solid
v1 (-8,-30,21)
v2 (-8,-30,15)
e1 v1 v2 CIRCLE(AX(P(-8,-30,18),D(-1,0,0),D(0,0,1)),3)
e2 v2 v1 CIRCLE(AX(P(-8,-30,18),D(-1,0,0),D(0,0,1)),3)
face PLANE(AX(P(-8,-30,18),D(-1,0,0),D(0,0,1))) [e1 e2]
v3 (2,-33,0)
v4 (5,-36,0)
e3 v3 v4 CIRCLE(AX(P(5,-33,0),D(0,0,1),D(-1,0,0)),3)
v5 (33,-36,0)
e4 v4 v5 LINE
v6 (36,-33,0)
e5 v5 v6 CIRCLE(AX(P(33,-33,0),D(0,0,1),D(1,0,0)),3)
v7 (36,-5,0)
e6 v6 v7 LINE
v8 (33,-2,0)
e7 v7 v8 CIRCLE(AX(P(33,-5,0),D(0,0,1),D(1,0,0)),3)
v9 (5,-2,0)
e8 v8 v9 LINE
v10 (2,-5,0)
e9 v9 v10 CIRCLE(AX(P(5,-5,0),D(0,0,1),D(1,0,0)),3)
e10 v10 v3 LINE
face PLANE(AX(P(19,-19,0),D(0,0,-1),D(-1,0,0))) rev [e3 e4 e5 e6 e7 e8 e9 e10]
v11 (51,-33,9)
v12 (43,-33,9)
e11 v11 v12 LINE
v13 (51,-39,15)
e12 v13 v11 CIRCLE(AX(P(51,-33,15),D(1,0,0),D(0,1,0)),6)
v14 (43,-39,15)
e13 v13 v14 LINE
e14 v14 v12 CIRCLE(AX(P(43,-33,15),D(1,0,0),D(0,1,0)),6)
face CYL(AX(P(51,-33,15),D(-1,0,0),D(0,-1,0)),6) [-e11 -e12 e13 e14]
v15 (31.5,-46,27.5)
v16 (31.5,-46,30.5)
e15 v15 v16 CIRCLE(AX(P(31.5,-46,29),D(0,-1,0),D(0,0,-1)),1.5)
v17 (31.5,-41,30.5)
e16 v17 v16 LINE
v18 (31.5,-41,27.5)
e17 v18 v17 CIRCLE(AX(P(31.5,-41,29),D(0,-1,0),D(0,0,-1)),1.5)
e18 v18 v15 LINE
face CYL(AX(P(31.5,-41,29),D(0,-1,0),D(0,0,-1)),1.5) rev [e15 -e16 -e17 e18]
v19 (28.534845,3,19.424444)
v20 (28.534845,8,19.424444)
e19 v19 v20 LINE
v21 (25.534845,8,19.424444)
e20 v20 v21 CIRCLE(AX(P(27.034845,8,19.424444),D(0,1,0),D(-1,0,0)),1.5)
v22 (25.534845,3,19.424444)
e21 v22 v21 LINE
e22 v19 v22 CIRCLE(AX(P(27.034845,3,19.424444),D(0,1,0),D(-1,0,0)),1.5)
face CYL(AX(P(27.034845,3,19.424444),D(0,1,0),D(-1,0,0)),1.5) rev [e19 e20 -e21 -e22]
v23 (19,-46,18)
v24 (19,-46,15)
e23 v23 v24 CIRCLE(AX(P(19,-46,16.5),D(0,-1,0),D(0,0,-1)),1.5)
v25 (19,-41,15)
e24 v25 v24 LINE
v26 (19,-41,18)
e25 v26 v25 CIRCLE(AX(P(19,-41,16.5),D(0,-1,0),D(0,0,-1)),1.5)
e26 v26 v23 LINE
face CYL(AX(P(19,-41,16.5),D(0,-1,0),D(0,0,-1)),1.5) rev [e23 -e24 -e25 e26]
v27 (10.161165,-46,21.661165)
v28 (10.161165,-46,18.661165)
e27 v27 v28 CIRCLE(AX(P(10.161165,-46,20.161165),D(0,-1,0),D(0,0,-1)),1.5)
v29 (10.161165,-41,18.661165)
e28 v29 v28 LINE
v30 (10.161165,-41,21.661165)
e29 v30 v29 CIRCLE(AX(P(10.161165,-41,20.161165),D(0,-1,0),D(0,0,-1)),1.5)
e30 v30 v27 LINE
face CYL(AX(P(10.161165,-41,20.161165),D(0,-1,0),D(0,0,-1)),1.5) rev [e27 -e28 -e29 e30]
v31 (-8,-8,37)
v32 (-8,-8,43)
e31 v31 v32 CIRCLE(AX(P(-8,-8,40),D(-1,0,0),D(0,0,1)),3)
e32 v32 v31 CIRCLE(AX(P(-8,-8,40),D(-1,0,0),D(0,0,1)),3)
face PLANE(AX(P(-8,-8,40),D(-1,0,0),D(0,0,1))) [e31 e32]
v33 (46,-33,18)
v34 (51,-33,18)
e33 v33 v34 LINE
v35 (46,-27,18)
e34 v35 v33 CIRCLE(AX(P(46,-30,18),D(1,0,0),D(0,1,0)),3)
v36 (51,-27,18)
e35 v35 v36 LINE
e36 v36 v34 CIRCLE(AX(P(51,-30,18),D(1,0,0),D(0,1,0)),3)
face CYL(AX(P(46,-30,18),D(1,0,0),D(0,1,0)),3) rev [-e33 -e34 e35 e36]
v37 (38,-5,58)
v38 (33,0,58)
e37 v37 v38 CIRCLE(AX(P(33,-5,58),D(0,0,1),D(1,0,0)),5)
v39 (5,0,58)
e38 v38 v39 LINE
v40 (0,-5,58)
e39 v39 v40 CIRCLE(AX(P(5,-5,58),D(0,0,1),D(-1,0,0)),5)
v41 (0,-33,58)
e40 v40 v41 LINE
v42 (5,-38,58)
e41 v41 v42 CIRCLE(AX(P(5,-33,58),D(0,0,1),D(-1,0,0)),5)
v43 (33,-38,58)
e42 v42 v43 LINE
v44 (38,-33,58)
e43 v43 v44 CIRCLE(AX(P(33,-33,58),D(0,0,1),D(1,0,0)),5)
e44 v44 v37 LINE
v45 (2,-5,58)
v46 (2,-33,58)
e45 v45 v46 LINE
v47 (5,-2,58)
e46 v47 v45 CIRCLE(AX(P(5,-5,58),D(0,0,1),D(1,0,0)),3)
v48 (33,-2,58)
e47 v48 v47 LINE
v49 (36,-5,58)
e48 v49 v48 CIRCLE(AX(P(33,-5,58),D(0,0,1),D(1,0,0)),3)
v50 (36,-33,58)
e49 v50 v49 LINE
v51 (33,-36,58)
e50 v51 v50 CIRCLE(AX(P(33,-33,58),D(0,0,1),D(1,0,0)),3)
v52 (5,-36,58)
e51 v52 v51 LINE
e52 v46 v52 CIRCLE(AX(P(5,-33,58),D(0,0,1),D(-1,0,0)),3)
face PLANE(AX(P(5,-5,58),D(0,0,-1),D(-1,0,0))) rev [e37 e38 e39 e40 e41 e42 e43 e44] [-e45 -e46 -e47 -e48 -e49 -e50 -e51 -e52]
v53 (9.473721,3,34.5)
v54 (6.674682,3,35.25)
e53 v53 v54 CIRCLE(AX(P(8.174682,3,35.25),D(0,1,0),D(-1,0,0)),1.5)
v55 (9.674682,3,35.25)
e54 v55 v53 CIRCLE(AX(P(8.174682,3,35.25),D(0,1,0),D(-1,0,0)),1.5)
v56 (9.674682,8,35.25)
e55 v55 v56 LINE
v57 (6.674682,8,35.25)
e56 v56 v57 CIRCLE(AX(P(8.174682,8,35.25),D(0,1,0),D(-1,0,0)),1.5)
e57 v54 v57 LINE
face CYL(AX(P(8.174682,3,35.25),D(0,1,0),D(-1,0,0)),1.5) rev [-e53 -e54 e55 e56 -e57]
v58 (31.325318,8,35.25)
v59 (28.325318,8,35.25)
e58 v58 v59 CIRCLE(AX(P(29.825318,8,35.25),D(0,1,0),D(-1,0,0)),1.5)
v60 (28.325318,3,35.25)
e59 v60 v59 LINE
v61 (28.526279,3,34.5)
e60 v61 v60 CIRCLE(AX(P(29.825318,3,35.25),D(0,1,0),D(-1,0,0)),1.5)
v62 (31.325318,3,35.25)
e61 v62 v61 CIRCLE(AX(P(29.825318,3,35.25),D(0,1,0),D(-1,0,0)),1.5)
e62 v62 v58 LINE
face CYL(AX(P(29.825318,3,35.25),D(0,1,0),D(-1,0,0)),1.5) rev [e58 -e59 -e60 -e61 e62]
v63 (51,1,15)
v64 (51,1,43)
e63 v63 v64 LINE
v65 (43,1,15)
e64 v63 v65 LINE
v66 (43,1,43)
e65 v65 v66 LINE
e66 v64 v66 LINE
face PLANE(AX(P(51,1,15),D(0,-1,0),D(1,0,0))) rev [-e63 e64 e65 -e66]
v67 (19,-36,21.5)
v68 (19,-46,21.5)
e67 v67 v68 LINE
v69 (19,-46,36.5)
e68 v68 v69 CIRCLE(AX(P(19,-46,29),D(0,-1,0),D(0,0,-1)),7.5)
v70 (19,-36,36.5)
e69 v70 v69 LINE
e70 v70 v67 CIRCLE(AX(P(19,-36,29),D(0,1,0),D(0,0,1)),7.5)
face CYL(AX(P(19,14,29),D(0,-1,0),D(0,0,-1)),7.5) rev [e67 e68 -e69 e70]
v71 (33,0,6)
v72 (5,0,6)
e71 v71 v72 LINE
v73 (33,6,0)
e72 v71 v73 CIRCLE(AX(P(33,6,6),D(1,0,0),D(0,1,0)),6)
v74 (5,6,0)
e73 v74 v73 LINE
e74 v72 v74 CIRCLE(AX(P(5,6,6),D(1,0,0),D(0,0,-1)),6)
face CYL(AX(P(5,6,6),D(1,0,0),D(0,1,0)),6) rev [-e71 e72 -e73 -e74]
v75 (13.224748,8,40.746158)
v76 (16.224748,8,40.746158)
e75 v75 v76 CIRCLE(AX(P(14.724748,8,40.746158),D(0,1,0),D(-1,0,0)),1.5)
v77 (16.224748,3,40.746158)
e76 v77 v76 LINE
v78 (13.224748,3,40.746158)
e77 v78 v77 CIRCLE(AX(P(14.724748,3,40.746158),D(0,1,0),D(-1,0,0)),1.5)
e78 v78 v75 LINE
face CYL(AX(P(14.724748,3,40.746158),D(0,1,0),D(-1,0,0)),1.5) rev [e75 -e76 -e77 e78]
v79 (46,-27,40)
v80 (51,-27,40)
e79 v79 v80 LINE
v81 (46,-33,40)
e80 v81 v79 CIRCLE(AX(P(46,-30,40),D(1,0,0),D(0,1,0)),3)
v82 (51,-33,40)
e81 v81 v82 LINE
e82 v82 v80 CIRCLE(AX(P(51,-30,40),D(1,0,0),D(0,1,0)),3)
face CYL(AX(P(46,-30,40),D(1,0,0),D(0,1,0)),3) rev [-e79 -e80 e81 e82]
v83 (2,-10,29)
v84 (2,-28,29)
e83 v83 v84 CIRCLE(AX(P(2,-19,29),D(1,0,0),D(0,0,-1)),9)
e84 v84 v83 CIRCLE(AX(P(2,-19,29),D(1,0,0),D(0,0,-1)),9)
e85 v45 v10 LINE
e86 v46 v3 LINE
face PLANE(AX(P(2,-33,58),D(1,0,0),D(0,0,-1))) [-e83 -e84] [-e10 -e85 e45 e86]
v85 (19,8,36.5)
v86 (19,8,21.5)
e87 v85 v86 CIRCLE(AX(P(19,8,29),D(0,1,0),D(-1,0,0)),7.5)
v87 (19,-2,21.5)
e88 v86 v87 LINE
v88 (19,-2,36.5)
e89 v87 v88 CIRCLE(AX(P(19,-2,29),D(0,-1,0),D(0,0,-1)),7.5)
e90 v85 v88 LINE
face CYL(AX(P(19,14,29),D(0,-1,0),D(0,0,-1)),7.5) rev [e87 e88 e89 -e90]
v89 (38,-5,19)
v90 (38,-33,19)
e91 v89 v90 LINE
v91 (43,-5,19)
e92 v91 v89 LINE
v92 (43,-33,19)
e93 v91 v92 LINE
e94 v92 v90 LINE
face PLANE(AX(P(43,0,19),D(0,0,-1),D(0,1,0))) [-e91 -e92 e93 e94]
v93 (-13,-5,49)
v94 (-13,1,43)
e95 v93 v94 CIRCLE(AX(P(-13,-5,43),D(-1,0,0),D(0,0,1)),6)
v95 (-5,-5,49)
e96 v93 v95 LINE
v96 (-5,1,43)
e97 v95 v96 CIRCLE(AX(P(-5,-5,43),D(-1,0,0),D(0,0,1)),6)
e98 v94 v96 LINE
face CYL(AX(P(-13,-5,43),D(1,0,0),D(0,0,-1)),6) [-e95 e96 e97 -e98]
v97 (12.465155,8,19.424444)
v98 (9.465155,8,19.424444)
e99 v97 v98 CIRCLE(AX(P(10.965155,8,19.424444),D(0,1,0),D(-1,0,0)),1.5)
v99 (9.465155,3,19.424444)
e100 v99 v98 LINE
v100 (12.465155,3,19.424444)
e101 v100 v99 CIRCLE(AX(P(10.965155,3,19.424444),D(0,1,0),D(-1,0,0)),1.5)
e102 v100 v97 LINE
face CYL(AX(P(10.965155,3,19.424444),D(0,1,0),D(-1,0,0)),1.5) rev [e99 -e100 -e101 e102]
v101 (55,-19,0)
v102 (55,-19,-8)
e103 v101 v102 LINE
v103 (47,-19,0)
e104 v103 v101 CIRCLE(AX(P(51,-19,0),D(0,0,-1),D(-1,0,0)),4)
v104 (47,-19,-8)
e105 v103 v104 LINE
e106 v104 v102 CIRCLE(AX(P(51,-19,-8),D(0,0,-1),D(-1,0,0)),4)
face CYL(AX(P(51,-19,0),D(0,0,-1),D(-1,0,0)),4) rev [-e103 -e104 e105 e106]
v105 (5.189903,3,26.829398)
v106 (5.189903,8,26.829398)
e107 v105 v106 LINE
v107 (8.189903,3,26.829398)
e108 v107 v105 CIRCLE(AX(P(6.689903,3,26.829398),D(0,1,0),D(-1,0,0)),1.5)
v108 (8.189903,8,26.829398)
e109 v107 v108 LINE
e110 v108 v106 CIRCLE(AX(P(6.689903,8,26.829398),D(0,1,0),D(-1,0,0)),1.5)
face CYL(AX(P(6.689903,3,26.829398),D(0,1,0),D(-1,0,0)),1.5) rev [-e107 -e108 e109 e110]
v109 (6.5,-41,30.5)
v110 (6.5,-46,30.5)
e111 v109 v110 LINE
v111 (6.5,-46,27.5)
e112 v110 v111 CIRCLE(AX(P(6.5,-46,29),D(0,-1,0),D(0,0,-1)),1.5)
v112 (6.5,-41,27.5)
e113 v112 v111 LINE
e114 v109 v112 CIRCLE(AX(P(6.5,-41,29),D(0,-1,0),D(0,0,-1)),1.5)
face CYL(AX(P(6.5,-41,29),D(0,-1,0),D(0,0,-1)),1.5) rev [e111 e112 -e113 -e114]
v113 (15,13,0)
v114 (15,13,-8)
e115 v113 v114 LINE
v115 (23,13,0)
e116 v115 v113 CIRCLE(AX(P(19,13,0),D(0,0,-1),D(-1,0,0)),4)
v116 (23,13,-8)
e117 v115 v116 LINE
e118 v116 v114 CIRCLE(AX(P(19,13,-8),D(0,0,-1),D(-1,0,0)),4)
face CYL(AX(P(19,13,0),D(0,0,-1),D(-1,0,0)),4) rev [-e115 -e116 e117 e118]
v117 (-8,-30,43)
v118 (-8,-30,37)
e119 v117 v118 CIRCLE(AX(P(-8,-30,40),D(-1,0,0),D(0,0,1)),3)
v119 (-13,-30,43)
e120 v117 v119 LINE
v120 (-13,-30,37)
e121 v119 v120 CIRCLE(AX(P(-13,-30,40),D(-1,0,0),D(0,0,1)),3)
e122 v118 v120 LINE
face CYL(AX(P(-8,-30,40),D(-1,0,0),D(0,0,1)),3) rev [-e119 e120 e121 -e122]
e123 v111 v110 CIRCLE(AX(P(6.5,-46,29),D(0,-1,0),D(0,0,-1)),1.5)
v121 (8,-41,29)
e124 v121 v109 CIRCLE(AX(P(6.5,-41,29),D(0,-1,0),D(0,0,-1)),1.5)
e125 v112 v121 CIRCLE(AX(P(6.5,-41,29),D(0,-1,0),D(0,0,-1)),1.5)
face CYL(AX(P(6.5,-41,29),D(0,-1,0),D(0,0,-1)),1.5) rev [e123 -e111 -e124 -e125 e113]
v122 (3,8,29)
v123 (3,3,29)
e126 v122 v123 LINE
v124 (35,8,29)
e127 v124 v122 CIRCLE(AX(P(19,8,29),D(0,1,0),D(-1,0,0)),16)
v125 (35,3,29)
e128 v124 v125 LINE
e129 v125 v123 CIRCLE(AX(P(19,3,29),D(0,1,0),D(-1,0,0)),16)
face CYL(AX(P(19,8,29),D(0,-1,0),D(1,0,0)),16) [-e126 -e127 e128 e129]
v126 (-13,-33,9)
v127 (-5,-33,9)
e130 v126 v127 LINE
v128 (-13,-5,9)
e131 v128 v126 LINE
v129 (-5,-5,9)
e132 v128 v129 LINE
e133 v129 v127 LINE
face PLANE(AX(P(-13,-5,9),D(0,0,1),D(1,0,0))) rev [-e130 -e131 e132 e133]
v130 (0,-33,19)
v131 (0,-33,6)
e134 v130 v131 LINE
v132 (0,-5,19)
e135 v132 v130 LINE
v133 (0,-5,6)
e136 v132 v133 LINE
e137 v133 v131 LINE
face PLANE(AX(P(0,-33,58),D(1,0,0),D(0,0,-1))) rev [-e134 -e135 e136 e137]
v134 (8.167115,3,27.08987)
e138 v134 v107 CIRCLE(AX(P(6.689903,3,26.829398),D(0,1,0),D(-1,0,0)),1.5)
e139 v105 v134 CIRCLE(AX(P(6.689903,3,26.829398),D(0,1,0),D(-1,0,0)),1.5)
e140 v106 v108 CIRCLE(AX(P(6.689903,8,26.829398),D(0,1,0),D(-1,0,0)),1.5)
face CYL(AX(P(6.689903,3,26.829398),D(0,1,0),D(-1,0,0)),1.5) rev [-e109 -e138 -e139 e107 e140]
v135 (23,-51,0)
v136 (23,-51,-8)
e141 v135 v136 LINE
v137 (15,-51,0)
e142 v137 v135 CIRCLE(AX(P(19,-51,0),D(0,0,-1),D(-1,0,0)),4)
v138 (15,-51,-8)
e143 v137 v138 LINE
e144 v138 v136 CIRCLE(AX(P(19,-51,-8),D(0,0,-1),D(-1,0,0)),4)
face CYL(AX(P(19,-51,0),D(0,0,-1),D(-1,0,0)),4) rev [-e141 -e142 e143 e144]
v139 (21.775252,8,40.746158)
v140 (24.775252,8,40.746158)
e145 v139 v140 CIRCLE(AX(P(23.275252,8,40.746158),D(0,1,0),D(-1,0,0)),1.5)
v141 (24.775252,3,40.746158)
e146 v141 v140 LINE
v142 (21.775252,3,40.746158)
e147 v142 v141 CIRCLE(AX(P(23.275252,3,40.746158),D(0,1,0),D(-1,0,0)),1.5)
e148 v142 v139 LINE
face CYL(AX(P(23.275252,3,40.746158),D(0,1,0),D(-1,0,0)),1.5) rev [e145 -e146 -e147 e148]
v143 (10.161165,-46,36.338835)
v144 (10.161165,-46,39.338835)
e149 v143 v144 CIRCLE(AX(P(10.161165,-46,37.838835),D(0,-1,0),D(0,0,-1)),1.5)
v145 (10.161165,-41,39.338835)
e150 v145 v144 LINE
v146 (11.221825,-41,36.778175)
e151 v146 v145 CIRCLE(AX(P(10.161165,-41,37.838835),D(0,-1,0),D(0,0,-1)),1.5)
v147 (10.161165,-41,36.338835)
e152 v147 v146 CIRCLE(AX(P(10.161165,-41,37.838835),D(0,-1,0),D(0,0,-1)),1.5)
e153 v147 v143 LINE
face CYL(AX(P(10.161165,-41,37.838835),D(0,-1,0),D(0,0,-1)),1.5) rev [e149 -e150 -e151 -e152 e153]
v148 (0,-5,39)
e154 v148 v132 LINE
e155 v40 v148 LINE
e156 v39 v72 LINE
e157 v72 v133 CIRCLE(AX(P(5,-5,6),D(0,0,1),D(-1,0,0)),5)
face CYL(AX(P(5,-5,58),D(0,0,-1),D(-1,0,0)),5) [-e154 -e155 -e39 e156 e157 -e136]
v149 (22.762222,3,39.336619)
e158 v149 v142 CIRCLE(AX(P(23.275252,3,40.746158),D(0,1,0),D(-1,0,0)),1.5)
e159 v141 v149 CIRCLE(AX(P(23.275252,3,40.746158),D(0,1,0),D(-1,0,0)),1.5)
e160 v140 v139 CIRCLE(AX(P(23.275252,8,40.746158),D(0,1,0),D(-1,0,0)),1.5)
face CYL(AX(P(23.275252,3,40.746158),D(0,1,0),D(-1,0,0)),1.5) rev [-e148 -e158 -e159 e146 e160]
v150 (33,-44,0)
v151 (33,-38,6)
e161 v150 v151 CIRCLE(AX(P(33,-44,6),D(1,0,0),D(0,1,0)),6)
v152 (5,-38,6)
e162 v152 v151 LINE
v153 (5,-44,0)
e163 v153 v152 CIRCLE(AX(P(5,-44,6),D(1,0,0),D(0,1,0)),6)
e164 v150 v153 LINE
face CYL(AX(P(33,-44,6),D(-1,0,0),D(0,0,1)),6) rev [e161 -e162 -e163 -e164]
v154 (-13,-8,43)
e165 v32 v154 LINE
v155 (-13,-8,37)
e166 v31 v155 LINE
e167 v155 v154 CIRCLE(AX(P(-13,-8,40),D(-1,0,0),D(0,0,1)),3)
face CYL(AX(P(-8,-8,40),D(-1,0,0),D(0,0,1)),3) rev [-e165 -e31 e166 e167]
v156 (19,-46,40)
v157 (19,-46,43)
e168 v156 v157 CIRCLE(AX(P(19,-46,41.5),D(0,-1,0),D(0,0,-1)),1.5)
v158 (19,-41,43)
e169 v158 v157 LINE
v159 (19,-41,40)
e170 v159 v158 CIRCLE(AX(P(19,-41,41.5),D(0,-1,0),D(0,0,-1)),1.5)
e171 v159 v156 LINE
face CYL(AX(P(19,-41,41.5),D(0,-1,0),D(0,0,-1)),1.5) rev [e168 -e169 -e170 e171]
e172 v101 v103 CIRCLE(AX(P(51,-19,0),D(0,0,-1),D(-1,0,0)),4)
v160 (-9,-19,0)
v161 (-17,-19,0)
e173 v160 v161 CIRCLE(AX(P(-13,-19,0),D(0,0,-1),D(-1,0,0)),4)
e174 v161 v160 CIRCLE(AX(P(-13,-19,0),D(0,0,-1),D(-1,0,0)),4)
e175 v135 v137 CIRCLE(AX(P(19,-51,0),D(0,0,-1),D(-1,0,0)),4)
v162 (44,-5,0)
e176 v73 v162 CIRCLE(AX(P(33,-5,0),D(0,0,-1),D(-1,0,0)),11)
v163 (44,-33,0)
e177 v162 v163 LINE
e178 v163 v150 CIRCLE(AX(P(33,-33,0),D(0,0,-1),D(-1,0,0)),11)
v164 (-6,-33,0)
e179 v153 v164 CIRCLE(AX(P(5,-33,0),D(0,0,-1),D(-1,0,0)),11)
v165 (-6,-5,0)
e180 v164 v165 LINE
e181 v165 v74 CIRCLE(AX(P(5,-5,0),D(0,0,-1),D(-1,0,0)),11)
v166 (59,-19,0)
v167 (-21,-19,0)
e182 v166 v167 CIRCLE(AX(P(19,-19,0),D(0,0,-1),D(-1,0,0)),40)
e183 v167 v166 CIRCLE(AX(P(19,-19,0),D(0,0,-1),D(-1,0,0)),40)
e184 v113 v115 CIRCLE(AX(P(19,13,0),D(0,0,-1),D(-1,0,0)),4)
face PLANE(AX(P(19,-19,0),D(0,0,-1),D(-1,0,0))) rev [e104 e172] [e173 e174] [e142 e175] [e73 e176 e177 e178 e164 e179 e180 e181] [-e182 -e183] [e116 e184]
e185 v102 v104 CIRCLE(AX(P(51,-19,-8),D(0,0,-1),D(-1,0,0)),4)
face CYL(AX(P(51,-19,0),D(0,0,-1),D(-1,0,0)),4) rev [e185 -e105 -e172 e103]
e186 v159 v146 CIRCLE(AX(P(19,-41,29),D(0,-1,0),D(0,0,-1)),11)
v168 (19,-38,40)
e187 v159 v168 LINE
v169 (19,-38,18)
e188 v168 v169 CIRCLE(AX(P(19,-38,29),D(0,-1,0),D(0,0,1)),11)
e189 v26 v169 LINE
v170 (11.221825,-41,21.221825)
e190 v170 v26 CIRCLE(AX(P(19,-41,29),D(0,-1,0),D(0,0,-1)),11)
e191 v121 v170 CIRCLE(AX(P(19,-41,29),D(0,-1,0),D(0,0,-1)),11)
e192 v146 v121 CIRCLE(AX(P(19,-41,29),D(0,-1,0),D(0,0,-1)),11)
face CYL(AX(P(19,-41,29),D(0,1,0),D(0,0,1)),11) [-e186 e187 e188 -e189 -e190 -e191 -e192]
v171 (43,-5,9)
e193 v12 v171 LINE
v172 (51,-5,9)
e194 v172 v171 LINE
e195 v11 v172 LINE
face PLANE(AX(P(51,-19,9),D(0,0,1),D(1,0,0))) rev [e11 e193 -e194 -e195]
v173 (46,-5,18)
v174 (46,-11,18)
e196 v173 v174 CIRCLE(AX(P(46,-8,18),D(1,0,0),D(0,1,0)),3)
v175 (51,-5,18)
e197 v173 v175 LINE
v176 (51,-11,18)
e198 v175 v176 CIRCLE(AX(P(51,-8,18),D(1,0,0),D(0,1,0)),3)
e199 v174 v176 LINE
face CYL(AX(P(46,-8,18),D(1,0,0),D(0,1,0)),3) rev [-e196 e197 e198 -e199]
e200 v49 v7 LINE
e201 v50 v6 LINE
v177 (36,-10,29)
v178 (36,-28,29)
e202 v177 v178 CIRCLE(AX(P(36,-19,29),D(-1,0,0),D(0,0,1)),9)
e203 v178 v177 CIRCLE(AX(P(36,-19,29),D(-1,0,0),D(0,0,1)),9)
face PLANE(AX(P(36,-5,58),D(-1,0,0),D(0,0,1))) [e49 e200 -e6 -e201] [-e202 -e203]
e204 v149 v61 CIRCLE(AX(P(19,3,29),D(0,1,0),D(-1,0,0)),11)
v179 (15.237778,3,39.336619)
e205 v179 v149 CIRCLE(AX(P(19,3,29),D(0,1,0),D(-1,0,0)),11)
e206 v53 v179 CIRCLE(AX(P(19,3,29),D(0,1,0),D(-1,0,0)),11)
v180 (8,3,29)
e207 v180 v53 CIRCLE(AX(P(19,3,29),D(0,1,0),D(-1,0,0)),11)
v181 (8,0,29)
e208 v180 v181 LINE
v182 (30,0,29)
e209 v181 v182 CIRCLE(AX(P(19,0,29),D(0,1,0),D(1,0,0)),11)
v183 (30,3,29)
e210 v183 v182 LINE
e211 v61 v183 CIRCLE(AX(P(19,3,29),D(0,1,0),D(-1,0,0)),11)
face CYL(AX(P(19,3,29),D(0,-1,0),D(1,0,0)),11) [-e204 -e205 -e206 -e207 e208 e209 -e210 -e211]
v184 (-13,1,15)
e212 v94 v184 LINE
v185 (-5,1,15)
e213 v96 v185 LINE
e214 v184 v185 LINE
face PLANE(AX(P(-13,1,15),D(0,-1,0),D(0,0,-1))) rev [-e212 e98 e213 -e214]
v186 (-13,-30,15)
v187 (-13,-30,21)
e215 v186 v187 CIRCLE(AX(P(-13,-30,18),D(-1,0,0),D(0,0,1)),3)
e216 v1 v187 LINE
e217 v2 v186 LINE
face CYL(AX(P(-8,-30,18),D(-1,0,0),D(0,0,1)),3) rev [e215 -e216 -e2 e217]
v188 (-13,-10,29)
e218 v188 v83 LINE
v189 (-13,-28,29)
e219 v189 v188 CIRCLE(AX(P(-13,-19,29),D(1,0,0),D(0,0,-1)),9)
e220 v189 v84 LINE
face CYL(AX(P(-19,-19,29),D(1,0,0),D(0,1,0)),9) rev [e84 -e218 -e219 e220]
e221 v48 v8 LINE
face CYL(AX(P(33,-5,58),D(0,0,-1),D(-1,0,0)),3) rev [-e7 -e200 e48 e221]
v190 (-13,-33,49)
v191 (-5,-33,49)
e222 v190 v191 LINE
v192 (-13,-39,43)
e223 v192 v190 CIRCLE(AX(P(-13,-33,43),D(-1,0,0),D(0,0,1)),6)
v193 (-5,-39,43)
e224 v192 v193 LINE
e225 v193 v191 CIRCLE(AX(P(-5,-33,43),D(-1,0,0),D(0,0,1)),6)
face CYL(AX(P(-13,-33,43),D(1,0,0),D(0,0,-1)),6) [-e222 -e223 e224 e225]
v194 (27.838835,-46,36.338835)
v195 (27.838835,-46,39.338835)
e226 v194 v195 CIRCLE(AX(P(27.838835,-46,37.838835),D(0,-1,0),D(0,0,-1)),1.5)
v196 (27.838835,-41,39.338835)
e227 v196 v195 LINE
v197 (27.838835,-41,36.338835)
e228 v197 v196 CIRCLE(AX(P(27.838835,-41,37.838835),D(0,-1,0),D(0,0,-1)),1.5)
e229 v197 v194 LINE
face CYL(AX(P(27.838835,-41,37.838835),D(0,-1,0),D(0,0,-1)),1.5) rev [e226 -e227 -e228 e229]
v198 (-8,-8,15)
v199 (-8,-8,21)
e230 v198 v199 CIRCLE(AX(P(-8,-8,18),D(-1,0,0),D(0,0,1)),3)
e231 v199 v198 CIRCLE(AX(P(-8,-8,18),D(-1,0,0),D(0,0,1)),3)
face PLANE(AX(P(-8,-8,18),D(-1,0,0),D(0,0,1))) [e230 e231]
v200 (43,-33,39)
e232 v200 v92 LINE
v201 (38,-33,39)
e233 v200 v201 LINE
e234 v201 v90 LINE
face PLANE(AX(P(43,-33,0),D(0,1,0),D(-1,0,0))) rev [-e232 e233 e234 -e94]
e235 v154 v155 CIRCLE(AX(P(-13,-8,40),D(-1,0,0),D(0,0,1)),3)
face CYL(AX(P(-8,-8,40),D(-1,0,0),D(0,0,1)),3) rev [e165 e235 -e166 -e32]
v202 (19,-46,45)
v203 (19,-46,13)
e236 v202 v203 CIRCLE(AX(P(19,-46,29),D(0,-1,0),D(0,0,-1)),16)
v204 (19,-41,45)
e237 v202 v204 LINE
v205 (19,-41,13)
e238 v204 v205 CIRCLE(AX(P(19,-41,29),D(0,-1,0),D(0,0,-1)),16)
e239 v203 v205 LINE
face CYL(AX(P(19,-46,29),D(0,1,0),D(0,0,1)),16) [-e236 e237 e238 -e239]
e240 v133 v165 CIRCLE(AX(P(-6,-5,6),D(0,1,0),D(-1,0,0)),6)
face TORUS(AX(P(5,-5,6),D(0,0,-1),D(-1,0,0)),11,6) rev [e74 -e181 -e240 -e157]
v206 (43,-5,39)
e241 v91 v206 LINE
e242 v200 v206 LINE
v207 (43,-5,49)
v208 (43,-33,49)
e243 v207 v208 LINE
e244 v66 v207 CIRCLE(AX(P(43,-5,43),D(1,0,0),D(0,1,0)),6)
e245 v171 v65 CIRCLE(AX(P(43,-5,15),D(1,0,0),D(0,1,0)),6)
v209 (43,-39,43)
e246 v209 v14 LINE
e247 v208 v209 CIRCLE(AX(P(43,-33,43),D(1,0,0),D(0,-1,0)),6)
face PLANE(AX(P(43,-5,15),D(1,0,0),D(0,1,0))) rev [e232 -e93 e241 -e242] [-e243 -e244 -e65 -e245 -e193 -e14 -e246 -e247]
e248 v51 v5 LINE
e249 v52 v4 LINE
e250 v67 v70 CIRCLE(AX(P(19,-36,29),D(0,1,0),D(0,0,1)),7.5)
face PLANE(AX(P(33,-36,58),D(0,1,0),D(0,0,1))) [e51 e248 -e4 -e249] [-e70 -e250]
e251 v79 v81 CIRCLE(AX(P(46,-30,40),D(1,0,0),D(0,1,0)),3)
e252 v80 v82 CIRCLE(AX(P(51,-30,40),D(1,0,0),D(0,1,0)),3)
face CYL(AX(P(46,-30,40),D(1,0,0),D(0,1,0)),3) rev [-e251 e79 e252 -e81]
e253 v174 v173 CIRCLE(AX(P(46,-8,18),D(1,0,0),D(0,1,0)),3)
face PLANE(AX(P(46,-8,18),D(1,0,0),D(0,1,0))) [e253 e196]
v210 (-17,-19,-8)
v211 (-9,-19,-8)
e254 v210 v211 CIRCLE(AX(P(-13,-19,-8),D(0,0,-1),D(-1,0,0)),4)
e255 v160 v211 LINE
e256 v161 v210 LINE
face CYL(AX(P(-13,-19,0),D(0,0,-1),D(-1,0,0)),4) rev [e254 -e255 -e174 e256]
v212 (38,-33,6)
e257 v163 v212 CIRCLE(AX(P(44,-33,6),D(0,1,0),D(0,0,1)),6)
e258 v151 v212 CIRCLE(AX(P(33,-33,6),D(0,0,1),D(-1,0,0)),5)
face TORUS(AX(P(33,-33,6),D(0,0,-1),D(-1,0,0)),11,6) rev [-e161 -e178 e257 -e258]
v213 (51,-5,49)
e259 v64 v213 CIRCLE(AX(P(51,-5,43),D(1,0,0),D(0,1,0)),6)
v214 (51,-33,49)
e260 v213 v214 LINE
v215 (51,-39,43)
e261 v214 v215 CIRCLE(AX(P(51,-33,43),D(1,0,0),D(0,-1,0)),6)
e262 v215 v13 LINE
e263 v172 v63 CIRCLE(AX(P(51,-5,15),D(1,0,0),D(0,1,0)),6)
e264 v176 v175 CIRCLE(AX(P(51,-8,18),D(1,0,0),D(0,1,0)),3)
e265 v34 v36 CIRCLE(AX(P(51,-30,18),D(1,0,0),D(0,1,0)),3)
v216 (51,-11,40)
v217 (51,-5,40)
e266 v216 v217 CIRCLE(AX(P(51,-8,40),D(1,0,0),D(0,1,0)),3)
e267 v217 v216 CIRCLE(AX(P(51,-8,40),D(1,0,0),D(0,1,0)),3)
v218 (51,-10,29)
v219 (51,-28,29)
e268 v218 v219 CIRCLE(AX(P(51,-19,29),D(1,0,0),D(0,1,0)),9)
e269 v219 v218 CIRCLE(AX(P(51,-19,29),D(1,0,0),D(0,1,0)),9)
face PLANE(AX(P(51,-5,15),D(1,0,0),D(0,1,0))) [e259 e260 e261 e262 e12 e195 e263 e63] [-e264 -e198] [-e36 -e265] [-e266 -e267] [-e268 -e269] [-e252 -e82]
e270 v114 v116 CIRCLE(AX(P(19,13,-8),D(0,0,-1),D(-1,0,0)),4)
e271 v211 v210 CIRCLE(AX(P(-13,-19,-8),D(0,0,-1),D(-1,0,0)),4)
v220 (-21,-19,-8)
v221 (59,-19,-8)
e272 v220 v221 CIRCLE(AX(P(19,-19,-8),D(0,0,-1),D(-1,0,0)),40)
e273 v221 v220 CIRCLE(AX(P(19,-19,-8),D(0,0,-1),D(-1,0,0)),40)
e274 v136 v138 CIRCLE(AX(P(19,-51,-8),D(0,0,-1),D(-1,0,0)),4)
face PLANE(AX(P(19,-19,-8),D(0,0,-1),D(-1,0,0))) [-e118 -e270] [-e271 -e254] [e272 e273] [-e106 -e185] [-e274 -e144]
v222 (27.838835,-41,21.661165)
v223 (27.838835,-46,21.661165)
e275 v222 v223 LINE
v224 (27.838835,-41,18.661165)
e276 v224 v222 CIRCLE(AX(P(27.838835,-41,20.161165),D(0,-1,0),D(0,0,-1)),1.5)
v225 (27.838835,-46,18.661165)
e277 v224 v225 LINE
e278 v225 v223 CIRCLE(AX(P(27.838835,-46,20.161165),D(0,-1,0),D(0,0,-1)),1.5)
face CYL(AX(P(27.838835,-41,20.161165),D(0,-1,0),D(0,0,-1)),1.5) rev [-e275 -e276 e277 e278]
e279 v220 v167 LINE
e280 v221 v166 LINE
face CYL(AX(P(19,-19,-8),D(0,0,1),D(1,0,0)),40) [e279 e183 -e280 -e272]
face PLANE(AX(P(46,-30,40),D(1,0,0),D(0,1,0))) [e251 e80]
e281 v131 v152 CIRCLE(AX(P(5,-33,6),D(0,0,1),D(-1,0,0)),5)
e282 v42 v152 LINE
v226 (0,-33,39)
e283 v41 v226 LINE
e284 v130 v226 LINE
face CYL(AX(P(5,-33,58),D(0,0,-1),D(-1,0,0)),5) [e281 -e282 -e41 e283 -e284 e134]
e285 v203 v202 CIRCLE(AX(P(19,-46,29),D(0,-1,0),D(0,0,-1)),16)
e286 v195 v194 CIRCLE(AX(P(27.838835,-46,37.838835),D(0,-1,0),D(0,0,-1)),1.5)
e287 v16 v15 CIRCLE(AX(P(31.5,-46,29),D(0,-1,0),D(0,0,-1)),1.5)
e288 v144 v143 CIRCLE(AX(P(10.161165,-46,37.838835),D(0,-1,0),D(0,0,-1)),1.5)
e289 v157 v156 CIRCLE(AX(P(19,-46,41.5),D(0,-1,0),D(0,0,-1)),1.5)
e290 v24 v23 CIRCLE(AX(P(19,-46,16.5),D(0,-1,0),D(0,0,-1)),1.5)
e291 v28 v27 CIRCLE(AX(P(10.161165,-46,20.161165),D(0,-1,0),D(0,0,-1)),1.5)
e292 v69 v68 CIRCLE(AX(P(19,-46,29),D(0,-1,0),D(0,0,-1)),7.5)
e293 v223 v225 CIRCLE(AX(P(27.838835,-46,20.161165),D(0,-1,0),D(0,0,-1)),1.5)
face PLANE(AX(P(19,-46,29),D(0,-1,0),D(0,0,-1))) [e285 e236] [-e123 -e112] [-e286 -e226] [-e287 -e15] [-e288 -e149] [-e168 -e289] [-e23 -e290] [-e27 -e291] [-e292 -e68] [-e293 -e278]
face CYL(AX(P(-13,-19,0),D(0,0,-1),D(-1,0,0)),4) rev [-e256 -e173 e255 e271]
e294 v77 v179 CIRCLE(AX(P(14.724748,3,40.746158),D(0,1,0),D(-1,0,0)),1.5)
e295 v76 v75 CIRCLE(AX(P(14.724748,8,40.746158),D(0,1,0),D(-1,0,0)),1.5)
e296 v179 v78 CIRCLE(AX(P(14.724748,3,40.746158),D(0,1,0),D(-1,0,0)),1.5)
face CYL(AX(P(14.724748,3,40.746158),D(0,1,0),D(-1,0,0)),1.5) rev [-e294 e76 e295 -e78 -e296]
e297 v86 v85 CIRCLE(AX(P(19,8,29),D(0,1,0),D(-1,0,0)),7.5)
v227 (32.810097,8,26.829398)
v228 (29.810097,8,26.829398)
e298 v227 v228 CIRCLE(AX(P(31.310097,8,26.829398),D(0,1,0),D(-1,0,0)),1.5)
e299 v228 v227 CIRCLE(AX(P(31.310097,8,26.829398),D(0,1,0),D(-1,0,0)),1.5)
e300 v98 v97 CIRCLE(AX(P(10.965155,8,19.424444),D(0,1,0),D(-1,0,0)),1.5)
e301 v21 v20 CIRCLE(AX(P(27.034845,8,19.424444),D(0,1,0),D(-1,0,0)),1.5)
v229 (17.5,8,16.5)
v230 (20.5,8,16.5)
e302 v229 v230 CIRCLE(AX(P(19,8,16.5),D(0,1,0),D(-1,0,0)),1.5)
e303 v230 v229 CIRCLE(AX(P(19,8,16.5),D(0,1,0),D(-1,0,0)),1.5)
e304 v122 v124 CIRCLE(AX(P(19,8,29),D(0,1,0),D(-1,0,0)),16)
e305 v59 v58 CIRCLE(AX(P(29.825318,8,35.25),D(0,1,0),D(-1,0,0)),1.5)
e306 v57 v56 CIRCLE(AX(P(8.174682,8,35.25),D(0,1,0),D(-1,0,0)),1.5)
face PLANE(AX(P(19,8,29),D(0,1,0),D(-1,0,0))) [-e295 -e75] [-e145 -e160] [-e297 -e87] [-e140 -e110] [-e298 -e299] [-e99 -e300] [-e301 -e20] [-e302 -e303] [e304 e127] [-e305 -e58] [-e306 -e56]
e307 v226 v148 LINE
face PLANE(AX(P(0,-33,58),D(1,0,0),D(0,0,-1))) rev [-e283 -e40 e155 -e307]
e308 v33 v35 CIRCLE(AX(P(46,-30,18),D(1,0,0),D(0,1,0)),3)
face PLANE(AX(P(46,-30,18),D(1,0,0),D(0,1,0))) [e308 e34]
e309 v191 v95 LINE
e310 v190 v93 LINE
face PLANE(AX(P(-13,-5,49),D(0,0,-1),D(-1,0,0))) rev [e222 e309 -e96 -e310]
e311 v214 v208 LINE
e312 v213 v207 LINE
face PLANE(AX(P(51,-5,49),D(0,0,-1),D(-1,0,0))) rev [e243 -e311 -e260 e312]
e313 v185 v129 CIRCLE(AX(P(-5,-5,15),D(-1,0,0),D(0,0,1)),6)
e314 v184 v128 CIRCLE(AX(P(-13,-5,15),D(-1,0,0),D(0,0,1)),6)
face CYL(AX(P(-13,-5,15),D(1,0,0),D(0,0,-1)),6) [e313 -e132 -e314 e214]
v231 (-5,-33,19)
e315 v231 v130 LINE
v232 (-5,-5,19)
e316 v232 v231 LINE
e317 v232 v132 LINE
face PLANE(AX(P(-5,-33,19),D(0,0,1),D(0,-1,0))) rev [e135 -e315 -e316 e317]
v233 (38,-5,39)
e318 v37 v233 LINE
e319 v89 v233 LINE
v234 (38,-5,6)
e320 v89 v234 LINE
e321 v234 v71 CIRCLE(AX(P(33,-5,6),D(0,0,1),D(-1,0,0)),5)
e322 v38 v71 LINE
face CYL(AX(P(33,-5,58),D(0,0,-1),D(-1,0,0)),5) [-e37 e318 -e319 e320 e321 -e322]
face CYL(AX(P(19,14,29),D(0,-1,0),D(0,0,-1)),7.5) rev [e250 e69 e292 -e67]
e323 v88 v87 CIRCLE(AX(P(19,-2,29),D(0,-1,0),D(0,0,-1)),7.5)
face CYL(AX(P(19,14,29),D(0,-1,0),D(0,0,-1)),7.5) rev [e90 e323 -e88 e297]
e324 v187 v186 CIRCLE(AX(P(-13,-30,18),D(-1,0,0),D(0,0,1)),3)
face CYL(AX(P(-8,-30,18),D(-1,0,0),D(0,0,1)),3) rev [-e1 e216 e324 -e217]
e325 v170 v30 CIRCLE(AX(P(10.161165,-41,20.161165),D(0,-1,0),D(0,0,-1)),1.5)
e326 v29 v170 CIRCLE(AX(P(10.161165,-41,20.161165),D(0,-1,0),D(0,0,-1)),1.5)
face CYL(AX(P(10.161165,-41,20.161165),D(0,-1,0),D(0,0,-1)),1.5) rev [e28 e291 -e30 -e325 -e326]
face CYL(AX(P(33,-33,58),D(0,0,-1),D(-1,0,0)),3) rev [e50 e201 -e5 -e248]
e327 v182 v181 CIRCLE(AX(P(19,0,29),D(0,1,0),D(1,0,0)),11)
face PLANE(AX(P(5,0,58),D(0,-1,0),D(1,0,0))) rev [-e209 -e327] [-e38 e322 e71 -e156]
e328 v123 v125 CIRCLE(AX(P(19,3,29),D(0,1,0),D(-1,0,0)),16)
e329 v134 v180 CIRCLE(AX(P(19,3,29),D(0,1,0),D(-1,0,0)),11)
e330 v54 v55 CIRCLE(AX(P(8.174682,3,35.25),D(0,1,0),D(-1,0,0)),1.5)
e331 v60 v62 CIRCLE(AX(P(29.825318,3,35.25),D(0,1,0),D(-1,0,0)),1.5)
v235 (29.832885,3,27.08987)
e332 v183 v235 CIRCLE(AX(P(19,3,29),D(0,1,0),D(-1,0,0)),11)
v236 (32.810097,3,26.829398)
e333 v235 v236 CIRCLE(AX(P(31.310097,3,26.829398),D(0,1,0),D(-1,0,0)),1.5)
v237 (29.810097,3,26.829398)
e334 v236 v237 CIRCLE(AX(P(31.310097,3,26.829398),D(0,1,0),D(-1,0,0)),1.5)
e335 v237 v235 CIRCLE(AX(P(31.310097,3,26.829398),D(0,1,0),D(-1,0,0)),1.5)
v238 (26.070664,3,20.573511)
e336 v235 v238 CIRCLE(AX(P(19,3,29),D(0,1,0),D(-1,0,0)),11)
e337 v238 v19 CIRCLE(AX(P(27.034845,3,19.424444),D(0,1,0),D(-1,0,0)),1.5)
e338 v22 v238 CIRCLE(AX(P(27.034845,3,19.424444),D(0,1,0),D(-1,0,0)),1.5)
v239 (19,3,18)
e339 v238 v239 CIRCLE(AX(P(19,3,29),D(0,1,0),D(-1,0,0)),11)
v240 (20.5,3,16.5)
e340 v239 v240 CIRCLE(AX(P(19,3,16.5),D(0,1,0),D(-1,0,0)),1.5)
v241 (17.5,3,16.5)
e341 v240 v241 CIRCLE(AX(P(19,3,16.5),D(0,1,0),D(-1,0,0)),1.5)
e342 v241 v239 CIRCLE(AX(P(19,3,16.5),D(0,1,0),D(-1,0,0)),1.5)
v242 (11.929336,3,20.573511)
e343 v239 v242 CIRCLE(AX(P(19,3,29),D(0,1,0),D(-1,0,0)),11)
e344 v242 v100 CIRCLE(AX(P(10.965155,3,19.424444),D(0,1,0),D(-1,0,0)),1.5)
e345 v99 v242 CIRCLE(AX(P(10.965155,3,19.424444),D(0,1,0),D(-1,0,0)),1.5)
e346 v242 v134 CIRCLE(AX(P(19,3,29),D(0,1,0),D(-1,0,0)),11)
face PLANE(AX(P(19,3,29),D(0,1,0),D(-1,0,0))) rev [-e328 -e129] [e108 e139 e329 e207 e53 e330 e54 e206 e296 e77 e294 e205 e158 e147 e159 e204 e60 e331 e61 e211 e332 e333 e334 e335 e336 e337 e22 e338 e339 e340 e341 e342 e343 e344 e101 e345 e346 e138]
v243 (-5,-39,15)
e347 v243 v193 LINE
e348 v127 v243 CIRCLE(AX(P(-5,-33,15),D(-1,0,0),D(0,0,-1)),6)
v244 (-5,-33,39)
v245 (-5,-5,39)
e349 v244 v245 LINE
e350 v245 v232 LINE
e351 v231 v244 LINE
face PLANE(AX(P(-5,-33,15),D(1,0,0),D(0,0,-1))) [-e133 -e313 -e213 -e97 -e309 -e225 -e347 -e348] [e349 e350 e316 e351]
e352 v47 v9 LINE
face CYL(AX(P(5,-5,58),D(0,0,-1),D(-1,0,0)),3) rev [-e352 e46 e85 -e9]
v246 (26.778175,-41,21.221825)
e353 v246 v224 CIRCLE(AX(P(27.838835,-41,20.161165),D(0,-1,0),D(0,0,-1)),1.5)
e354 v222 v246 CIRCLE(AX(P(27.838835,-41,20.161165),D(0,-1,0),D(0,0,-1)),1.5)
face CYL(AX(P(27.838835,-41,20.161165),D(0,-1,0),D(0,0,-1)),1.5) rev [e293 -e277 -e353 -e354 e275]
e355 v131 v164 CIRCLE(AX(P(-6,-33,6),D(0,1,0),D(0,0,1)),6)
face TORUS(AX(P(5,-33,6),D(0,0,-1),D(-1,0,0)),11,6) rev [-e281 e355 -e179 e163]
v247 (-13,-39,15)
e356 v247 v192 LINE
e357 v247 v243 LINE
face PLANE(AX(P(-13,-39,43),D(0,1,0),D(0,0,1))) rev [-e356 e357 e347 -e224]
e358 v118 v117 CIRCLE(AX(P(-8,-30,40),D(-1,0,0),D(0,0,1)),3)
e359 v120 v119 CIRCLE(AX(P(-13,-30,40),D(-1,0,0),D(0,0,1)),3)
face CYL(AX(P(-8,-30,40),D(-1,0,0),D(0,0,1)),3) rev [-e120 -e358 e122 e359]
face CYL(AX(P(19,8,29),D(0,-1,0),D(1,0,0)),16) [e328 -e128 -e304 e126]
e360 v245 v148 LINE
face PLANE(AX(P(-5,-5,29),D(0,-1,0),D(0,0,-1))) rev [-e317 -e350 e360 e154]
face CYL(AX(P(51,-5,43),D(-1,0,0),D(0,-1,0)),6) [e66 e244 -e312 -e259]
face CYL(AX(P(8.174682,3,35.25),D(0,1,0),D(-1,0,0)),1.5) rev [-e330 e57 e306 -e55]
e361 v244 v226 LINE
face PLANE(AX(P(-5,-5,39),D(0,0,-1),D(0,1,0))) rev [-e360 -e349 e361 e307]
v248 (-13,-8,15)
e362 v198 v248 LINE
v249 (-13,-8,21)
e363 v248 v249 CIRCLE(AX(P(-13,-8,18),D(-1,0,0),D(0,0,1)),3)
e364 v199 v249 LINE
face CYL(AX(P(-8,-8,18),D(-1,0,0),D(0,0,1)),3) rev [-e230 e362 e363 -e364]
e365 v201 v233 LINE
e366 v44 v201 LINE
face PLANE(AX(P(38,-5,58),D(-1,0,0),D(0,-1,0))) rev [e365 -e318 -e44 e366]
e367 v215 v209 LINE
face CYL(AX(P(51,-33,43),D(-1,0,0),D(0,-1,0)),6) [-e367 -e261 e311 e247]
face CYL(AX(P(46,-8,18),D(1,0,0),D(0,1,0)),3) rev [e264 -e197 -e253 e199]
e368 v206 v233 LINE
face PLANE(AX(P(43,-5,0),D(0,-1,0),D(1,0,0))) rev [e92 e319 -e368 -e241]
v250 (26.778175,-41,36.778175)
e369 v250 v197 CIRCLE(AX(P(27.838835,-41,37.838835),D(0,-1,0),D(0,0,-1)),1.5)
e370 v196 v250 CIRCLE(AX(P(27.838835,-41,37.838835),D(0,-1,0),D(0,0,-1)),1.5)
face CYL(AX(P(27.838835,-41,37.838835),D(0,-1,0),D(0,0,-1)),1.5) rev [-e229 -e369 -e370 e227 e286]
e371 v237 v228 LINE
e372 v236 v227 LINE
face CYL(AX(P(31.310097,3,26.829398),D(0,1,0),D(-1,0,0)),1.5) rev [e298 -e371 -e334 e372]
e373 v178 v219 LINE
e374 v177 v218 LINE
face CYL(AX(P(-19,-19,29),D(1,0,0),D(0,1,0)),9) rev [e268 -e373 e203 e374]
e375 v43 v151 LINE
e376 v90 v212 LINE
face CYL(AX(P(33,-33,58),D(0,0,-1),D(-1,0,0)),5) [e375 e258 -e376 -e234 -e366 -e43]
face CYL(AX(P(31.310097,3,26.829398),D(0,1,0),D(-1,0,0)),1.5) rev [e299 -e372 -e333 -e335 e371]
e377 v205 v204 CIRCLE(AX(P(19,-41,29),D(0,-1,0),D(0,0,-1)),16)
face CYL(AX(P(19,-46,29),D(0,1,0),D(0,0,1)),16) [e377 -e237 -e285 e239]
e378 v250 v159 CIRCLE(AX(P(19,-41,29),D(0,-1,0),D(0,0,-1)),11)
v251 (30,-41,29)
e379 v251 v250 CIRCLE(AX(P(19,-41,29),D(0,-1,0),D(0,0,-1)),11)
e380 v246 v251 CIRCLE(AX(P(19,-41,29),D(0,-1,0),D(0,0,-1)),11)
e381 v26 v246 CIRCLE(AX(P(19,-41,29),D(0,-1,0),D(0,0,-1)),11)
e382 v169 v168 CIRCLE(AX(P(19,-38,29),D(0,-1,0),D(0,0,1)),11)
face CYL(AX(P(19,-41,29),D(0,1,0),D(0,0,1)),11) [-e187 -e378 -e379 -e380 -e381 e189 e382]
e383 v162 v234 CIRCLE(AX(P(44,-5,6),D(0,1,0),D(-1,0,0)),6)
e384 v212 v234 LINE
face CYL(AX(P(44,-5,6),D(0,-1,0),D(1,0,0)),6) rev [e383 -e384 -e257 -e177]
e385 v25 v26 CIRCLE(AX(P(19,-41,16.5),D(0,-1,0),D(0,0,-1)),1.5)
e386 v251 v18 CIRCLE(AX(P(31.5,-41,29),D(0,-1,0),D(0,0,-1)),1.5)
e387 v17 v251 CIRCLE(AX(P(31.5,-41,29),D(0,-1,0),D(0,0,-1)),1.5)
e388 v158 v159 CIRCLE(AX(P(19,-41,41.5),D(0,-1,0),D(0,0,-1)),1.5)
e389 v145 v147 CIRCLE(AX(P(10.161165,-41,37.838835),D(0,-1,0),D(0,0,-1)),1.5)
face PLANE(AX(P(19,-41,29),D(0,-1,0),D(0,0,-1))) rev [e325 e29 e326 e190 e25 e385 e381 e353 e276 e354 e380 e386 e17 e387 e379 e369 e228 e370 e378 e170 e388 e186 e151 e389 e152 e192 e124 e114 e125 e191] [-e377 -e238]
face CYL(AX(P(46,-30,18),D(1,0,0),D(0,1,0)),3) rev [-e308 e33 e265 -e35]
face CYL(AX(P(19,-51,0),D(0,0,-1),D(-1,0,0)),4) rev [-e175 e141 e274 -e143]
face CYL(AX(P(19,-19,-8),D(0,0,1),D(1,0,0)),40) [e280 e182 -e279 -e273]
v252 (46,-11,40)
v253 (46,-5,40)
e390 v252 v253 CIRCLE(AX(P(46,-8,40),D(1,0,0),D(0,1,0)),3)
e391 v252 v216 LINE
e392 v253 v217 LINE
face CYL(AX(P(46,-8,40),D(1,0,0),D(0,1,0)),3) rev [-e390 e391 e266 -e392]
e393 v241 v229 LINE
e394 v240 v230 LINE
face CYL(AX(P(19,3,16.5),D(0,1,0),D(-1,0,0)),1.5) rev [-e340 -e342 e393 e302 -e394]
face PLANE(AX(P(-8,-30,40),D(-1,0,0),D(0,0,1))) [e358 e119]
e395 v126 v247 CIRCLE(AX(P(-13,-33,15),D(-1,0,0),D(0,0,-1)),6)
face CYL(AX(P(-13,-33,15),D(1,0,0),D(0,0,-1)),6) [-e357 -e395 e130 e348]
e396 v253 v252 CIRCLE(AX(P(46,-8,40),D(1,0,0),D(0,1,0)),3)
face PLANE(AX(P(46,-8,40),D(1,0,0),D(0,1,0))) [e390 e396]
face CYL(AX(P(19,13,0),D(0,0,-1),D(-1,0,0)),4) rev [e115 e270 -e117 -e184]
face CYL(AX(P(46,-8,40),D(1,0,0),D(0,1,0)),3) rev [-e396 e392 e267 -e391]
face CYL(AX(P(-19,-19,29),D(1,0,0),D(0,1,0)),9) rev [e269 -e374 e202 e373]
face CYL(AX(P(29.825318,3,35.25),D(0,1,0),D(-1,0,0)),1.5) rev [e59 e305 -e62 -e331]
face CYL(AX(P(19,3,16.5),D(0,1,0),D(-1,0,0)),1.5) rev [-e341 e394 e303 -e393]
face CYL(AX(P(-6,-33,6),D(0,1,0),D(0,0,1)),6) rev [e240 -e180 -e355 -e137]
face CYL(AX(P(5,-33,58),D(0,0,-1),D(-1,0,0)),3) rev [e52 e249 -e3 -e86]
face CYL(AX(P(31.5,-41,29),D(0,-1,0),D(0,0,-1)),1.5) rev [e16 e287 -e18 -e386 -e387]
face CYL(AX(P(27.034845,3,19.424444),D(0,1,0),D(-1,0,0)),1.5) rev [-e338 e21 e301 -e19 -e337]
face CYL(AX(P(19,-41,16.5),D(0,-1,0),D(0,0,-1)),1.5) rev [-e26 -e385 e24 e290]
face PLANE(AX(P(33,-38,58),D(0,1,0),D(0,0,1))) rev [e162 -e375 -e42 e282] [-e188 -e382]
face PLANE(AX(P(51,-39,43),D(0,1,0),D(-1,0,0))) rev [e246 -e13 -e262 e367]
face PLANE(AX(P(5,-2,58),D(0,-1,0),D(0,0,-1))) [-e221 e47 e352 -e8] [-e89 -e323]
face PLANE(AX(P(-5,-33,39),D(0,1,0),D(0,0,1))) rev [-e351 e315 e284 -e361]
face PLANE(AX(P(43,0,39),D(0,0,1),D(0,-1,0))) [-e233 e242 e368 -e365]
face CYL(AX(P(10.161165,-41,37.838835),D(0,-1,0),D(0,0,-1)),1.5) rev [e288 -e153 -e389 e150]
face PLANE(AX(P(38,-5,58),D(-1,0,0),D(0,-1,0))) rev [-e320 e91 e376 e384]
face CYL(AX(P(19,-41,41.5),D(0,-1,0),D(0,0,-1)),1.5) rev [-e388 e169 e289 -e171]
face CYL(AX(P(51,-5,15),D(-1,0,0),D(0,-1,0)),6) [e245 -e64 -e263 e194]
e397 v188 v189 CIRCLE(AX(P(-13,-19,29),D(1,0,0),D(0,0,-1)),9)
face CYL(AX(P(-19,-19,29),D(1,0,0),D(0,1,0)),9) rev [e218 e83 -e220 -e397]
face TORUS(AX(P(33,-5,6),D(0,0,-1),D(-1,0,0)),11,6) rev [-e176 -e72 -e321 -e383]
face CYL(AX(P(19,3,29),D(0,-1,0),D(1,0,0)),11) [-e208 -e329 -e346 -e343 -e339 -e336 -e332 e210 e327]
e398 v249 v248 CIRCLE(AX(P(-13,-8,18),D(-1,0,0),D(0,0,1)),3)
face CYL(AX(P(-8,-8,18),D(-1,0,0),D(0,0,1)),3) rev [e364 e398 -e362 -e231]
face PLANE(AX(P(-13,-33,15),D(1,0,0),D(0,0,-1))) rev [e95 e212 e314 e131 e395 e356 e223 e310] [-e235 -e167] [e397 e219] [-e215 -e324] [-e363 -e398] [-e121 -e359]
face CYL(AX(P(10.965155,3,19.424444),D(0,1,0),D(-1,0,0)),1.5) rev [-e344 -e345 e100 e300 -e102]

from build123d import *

# Parameters (mm, degrees)
SQUARE_TUBE_BODY_38X38_DEPTH   = 58
BASE_FLANGE_SKETCH_R           = 40
BASE_FLANGE_80_DEPTH           = 8
SPACER_PAD_A_DEPTH             = 5
SPACER_PAD_B_DEPTH             = 5
SIDE_PLATE_A_40X40_DEPTH       = 8
SIDE_START                     = 8
SIDE_PLATE_B_40X40_DEPTH       = 8
PORT_NECK_B_SKETCH_R           = 11
PORT_NECK_B_22_DEPTH           = 3
PORT_START                     = 3
PORT_NECK_A_SKETCH_R           = 11
PORT_NECK_A_22_DEPTH           = 3
PORT_FLANGE_A_SKETCH_R         = 16
PORT_FLANGE_A_32_DEPTH         = 5
PORT_START_2                   = 5
PORT_FLANGE_B_SKETCH_R         = 16
PORT_FLANGE_B_32_DEPTH         = 5
PORT_FLANGE_A_HOLES_SKETCH_R   = 1.5
PORT_FLANGE_A_HOLES_8X_3_DEPTH = 5
PORT_BORE_SKETCH_R             = 7.5
PORT_BORE_15_DEPTH             = 60
PORT_START_3                   = -5
PORT_FLANGE_B_HOLES_SKETCH_R   = 1.5
PORT_FLANGE_B_HOLES_9X_3_DEPTH = 5
SIDE_PLATE_BORE_SKETCH_R       = 9
SIDE_PLATE_BORE_18_DEPTH       = 70
SIDE_PLATE_A_HOLES_SKETCH_R    = 3
SIDE_PLATE_A_HOLES_4X_6_DEPTH  = 5
SIDE_START_2                   = -5
SIDE_PLATE_B_HOLES_SKETCH_R    = 3
SIDE_PLATE_B_HOLES_4X_6_DEPTH  = 5
BASE_FLANGE_HOLES_SKETCH_R     = 4
BASE_FLANGE_HOLES_4X_8_DEPTH   = 8
TUBE_TO_FLANGE_FILLET_R6_R     = 6


with BuildPart() as part:
    # Square Tube Profile Sketch → Square Tube Body 38x38 (new body)
    with BuildSketch(Plane.XY):
        with BuildLine():
            Line((5, 0), (33, 0))
            ThreePointArc((33, 0), (36.535533906, -1.464466094), (38, -5))
            Line((38, -5), (38, -33))
            ThreePointArc((38, -33), (36.535533906, -36.535533906), (33, -38))
            Line((33, -38), (5, -38))
            ThreePointArc((5, -38), (1.464466094, -36.535533906), (0, -33))
            Line((0, -33), (0, -5))
            ThreePointArc((0, -5), (1.464466094, -1.464466094), (5, 0))
        make_face()
        with BuildLine():
            Line((5, -2), (33, -2))
            ThreePointArc((33, -2), (35.121320344, -2.878679656), (36, -5))
            Line((36, -5), (36, -33))
            ThreePointArc((36, -33), (35.121320344, -35.121320344), (33, -36))
            Line((33, -36), (5, -36))
            ThreePointArc((5, -36), (2.878679656, -35.121320344), (2, -33))
            Line((2, -33), (2, -5))
            ThreePointArc((2, -5), (2.878679656, -2.878679656), (5, -2))
        make_face(mode=Mode.SUBTRACT)
    extrude(amount=SQUARE_TUBE_BODY_38X38_DEPTH)

    # Base Flange Sketch → Base Flange Ø80 (add)
    with BuildSketch(Plane(origin=(0, 0, 0), x_dir=(-1, 0, 0), z_dir=(0, 0, -1))):
        with Locations((-19, -19)):
            Circle(BASE_FLANGE_SKETCH_R)
    extrude(amount=BASE_FLANGE_80_DEPTH)

    # Spacer Pad A Sketch → Spacer Pad A (add)
    with BuildSketch(Plane(origin=(38, 0, 0), x_dir=(0, 0, -1), z_dir=(1, 0, 0))):
        Polygon((-19, -5), (-29, -5), (-39, -5), (-39, -33), (-19, -33), align=None)
    extrude(amount=SPACER_PAD_A_DEPTH)

    # Spacer Pad B Sketch → Spacer Pad B (add)
    with BuildSketch(Plane.ZY):
        Polygon((29, -5), (39, -5), (39, -33), (19, -33), (19, -5), align=None)
    extrude(amount=SPACER_PAD_B_DEPTH)

    # Side Plate A Sketch → Side Plate A 40x40 (add)
    with BuildSketch(Plane(origin=(43, 0, 0), x_dir=(0, 0, -1), z_dir=(1, 0, 0))):
        with BuildLine():
            Line((-9, -19), (-9, -5))
            ThreePointArc((-9, -5), (-10.757359313, -0.757359313), (-15, 1))
            Line((-15, 1), (-43, 1))
            ThreePointArc((-43, 1), (-47.242640687, -0.757359313), (-49, -5))
            Line((-49, -5), (-49, -33))
            ThreePointArc((-49, -33), (-47.242640687, -37.242640687), (-43, -39))
            Line((-43, -39), (-15, -39))
            ThreePointArc((-15, -39), (-10.757359313, -37.242640687), (-9, -33))
            Line((-9, -33), (-9, -19))
        make_face()
    extrude(amount=SIDE_PLATE_A_40X40_DEPTH)

    # Side Plate B Sketch → Side Plate B 40x40 (add)
    with BuildSketch(Plane.ZY.offset(5).offset(SIDE_START)):
        with BuildLine():
            Line((9, -5), (9, -33))
            ThreePointArc((9, -33), (10.757359313, -37.242640687), (15, -39))
            Line((15, -39), (43, -39))
            ThreePointArc((43, -39), (47.242640687, -37.242640687), (49, -33))
            Line((49, -33), (49, -5))
            ThreePointArc((49, -5), (47.242640687, -0.757359313), (43, 1))
            Line((43, 1), (15, 1))
            ThreePointArc((15, 1), (10.757359313, -0.757359313), (9, -5))
        make_face()
    extrude(amount=-SIDE_PLATE_B_40X40_DEPTH)

    # Port Neck B Sketch → Port Neck B Ø22 (add)
    with BuildSketch(Plane(origin=(0, 0, 0), x_dir=(1, 0, 0), z_dir=(0, 1, 0))):
        with Locations((19, -29)):
            Circle(PORT_NECK_B_SKETCH_R)
    extrude(amount=PORT_NECK_B_22_DEPTH)

    # Port Neck A Sketch → Port Neck A Ø22 (add)
    with BuildSketch(Plane.XZ.offset(38).offset(PORT_START)):
        with Locations((19, 29)):
            Circle(PORT_NECK_A_SKETCH_R)
    extrude(amount=-PORT_NECK_A_22_DEPTH)

    # Port Flange A Sketch → Port Flange A Ø32 (add)
    with BuildSketch(Plane.XZ.offset(41)):
        with Locations(Location((19, 29, 0), (0, 0, 270))):
            Circle(PORT_FLANGE_A_SKETCH_R)
    extrude(amount=PORT_FLANGE_A_32_DEPTH)

    # Port Flange B Sketch → Port Flange B Ø32 (add)
    with BuildSketch(Plane(origin=(0, 3, 0), x_dir=(1, 0, 0), z_dir=(0, 1, 0)).offset(PORT_START_2)):
        with Locations(Location((19, -29, 0), (0, 0, 90))):
            Circle(PORT_FLANGE_B_SKETCH_R)
    extrude(amount=-PORT_FLANGE_B_32_DEPTH)

    # Port Flange A Holes Sketch → Port Flange A Holes 8xØ3 (cut)
    with BuildSketch(Plane.XZ.offset(46)):
        with Locations(Location((31.5, 29, 0), (0, 0, 270))):
            Circle(PORT_FLANGE_A_HOLES_SKETCH_R)
        with Locations(Location((27.838834765, 20.161165235, 0), (0, 0, 270))):
            Circle(PORT_FLANGE_A_HOLES_SKETCH_R)
        with Locations(Location((19, 16.5, 0), (0, 0, 270))):
            Circle(PORT_FLANGE_A_HOLES_SKETCH_R)
        with Locations(Location((10.161165235, 20.161165235, 0), (0, 0, 270))):
            Circle(PORT_FLANGE_A_HOLES_SKETCH_R)
        with Locations(Location((6.5, 29, 0), (0, 0, 270))):
            Circle(PORT_FLANGE_A_HOLES_SKETCH_R)
        with Locations(Location((10.161165235, 37.838834765, 0), (0, 0, 270))):
            Circle(PORT_FLANGE_A_HOLES_SKETCH_R)
        with Locations(Location((19, 41.5, 0), (0, 0, 270))):
            Circle(PORT_FLANGE_A_HOLES_SKETCH_R)
        with Locations(Location((27.838834765, 37.838834765, 0), (0, 0, 270))):
            Circle(PORT_FLANGE_A_HOLES_SKETCH_R)
    extrude(amount=-PORT_FLANGE_A_HOLES_8X_3_DEPTH, mode=Mode.SUBTRACT)

    # Port Bore Sketch → Port Bore Ø15 (cut)
    with BuildSketch(Plane.XZ.offset(46)):
        with Locations(Location((19, 29, 0), (0, 0, 270))):
            Circle(PORT_BORE_SKETCH_R)
    extrude(amount=-PORT_BORE_15_DEPTH, mode=Mode.SUBTRACT)

    # Port Flange B Holes Sketch → Port Flange B Holes 9xØ3 (cut)
    with BuildSketch(Plane(origin=(0, 8, 0), x_dir=(1, 0, 0), z_dir=(0, 1, 0)).offset(PORT_START_3)):
        with Locations(Location((19, -16.5, 0), (0, 0, 90))):
            Circle(PORT_FLANGE_B_HOLES_SKETCH_R)
        with Locations(Location((27.034845121, -19.424444461, 0), (0, 0, 180))):
            Circle(PORT_FLANGE_B_HOLES_SKETCH_R)
        with Locations(Location((31.310096913, -26.829397779, 0), (0, 0, 180))):
            Circle(PORT_FLANGE_B_HOLES_SKETCH_R)
        with Locations(Location((29.825317547, -35.25, 0), (0, 0, 180))):
            Circle(PORT_FLANGE_B_HOLES_SKETCH_R)
        with Locations(Location((23.275251792, -40.74615776, 0), (0, 0, 180))):
            Circle(PORT_FLANGE_B_HOLES_SKETCH_R)
        with Locations(Location((14.724748208, -40.74615776, 0), (0, 0, 180))):
            Circle(PORT_FLANGE_B_HOLES_SKETCH_R)
        with Locations(Location((8.174682453, -35.25, 0), (0, 0, 180))):
            Circle(PORT_FLANGE_B_HOLES_SKETCH_R)
        with Locations(Location((6.689903087, -26.829397779, 0), (0, 0, 180))):
            Circle(PORT_FLANGE_B_HOLES_SKETCH_R)
        with Locations(Location((10.965154879, -19.424444461, 0), (0, 0, 180))):
            Circle(PORT_FLANGE_B_HOLES_SKETCH_R)
    extrude(amount=PORT_FLANGE_B_HOLES_9X_3_DEPTH, mode=Mode.SUBTRACT)

    # Side Plate Bore Sketch → Side Plate Bore Ø18 (cut)
    with BuildSketch(Plane(origin=(51, 0, 0), x_dir=(0, 0, -1), z_dir=(1, 0, 0))):
        with Locations((-29, -19)):
            Circle(SIDE_PLATE_BORE_SKETCH_R)
    extrude(amount=-SIDE_PLATE_BORE_18_DEPTH, mode=Mode.SUBTRACT)

    # Side Plate A Holes Sketch → Side Plate A Holes 4xØ6 (cut)
    with BuildSketch(Plane(origin=(51, 0, 0), x_dir=(0, 0, -1), z_dir=(1, 0, 0))):
        with Locations(Location((-18, -8, 0), (0, 0, 90))):
            Circle(SIDE_PLATE_A_HOLES_SKETCH_R)
        with Locations(Location((-40, -30, 0), (0, 0, 90))):
            Circle(SIDE_PLATE_A_HOLES_SKETCH_R)
        with Locations(Location((-18, -30, 0), (0, 0, 90))):
            Circle(SIDE_PLATE_A_HOLES_SKETCH_R)
        with Locations(Location((-40, -8, 0), (0, 0, 90))):
            Circle(SIDE_PLATE_A_HOLES_SKETCH_R)
    extrude(amount=-SIDE_PLATE_A_HOLES_4X_6_DEPTH, mode=Mode.SUBTRACT)

    # Side Plate B Holes Sketch → Side Plate B Holes 4xØ6 (cut)
    with BuildSketch(Plane.ZY.offset(13).offset(SIDE_START_2)):
        with Locations(Location((18, -8, 0), (0, 0, 90))):
            Circle(SIDE_PLATE_B_HOLES_SKETCH_R)
        with Locations(Location((40, -8, 0), (0, 0, 90))):
            Circle(SIDE_PLATE_B_HOLES_SKETCH_R)
        with Locations(Location((40, -30, 0), (0, 0, 90))):
            Circle(SIDE_PLATE_B_HOLES_SKETCH_R)
        with Locations(Location((18, -30, 0), (0, 0, 90))):
            Circle(SIDE_PLATE_B_HOLES_SKETCH_R)
    extrude(amount=SIDE_PLATE_B_HOLES_4X_6_DEPTH, mode=Mode.SUBTRACT)

    # Base Flange Holes Sketch → Base Flange Holes 4xØ8 (cut)
    with BuildSketch(Plane(origin=(0, 0, -8), x_dir=(-1, 0, 0), z_dir=(0, 0, -1))):
        with Locations((-19, 13)):
            Circle(BASE_FLANGE_HOLES_SKETCH_R)
        with Locations((13, -19)):
            Circle(BASE_FLANGE_HOLES_SKETCH_R)
        with Locations((-19, -51)):
            Circle(BASE_FLANGE_HOLES_SKETCH_R)
        with Locations((-51, -19)):
            Circle(BASE_FLANGE_HOLES_SKETCH_R)
    extrude(amount=-BASE_FLANGE_HOLES_4X_8_DEPTH, mode=Mode.SUBTRACT)

    # Tube-to-Flange Fillet R6
    tube_to_flange_fillet_r6_edges = [part.edges().sort_by_distance(p)[0] for p in [
        (19, -38, 0),
        (1.464466094, -36.535533906, 0),
        (0, -19, 0),
        (1.464466094, -1.464466094, 0),
        (19, 0, 0),
        (36.535533906, -1.464466094, 0),
        (38, -19, 0),
        (36.535533906, -36.535533906, 0),
    ]]
    fillet(tube_to_flange_fillet_r6_edges, radius=TUBE_TO_FLANGE_FILLET_R6_R)


solid = part.part
